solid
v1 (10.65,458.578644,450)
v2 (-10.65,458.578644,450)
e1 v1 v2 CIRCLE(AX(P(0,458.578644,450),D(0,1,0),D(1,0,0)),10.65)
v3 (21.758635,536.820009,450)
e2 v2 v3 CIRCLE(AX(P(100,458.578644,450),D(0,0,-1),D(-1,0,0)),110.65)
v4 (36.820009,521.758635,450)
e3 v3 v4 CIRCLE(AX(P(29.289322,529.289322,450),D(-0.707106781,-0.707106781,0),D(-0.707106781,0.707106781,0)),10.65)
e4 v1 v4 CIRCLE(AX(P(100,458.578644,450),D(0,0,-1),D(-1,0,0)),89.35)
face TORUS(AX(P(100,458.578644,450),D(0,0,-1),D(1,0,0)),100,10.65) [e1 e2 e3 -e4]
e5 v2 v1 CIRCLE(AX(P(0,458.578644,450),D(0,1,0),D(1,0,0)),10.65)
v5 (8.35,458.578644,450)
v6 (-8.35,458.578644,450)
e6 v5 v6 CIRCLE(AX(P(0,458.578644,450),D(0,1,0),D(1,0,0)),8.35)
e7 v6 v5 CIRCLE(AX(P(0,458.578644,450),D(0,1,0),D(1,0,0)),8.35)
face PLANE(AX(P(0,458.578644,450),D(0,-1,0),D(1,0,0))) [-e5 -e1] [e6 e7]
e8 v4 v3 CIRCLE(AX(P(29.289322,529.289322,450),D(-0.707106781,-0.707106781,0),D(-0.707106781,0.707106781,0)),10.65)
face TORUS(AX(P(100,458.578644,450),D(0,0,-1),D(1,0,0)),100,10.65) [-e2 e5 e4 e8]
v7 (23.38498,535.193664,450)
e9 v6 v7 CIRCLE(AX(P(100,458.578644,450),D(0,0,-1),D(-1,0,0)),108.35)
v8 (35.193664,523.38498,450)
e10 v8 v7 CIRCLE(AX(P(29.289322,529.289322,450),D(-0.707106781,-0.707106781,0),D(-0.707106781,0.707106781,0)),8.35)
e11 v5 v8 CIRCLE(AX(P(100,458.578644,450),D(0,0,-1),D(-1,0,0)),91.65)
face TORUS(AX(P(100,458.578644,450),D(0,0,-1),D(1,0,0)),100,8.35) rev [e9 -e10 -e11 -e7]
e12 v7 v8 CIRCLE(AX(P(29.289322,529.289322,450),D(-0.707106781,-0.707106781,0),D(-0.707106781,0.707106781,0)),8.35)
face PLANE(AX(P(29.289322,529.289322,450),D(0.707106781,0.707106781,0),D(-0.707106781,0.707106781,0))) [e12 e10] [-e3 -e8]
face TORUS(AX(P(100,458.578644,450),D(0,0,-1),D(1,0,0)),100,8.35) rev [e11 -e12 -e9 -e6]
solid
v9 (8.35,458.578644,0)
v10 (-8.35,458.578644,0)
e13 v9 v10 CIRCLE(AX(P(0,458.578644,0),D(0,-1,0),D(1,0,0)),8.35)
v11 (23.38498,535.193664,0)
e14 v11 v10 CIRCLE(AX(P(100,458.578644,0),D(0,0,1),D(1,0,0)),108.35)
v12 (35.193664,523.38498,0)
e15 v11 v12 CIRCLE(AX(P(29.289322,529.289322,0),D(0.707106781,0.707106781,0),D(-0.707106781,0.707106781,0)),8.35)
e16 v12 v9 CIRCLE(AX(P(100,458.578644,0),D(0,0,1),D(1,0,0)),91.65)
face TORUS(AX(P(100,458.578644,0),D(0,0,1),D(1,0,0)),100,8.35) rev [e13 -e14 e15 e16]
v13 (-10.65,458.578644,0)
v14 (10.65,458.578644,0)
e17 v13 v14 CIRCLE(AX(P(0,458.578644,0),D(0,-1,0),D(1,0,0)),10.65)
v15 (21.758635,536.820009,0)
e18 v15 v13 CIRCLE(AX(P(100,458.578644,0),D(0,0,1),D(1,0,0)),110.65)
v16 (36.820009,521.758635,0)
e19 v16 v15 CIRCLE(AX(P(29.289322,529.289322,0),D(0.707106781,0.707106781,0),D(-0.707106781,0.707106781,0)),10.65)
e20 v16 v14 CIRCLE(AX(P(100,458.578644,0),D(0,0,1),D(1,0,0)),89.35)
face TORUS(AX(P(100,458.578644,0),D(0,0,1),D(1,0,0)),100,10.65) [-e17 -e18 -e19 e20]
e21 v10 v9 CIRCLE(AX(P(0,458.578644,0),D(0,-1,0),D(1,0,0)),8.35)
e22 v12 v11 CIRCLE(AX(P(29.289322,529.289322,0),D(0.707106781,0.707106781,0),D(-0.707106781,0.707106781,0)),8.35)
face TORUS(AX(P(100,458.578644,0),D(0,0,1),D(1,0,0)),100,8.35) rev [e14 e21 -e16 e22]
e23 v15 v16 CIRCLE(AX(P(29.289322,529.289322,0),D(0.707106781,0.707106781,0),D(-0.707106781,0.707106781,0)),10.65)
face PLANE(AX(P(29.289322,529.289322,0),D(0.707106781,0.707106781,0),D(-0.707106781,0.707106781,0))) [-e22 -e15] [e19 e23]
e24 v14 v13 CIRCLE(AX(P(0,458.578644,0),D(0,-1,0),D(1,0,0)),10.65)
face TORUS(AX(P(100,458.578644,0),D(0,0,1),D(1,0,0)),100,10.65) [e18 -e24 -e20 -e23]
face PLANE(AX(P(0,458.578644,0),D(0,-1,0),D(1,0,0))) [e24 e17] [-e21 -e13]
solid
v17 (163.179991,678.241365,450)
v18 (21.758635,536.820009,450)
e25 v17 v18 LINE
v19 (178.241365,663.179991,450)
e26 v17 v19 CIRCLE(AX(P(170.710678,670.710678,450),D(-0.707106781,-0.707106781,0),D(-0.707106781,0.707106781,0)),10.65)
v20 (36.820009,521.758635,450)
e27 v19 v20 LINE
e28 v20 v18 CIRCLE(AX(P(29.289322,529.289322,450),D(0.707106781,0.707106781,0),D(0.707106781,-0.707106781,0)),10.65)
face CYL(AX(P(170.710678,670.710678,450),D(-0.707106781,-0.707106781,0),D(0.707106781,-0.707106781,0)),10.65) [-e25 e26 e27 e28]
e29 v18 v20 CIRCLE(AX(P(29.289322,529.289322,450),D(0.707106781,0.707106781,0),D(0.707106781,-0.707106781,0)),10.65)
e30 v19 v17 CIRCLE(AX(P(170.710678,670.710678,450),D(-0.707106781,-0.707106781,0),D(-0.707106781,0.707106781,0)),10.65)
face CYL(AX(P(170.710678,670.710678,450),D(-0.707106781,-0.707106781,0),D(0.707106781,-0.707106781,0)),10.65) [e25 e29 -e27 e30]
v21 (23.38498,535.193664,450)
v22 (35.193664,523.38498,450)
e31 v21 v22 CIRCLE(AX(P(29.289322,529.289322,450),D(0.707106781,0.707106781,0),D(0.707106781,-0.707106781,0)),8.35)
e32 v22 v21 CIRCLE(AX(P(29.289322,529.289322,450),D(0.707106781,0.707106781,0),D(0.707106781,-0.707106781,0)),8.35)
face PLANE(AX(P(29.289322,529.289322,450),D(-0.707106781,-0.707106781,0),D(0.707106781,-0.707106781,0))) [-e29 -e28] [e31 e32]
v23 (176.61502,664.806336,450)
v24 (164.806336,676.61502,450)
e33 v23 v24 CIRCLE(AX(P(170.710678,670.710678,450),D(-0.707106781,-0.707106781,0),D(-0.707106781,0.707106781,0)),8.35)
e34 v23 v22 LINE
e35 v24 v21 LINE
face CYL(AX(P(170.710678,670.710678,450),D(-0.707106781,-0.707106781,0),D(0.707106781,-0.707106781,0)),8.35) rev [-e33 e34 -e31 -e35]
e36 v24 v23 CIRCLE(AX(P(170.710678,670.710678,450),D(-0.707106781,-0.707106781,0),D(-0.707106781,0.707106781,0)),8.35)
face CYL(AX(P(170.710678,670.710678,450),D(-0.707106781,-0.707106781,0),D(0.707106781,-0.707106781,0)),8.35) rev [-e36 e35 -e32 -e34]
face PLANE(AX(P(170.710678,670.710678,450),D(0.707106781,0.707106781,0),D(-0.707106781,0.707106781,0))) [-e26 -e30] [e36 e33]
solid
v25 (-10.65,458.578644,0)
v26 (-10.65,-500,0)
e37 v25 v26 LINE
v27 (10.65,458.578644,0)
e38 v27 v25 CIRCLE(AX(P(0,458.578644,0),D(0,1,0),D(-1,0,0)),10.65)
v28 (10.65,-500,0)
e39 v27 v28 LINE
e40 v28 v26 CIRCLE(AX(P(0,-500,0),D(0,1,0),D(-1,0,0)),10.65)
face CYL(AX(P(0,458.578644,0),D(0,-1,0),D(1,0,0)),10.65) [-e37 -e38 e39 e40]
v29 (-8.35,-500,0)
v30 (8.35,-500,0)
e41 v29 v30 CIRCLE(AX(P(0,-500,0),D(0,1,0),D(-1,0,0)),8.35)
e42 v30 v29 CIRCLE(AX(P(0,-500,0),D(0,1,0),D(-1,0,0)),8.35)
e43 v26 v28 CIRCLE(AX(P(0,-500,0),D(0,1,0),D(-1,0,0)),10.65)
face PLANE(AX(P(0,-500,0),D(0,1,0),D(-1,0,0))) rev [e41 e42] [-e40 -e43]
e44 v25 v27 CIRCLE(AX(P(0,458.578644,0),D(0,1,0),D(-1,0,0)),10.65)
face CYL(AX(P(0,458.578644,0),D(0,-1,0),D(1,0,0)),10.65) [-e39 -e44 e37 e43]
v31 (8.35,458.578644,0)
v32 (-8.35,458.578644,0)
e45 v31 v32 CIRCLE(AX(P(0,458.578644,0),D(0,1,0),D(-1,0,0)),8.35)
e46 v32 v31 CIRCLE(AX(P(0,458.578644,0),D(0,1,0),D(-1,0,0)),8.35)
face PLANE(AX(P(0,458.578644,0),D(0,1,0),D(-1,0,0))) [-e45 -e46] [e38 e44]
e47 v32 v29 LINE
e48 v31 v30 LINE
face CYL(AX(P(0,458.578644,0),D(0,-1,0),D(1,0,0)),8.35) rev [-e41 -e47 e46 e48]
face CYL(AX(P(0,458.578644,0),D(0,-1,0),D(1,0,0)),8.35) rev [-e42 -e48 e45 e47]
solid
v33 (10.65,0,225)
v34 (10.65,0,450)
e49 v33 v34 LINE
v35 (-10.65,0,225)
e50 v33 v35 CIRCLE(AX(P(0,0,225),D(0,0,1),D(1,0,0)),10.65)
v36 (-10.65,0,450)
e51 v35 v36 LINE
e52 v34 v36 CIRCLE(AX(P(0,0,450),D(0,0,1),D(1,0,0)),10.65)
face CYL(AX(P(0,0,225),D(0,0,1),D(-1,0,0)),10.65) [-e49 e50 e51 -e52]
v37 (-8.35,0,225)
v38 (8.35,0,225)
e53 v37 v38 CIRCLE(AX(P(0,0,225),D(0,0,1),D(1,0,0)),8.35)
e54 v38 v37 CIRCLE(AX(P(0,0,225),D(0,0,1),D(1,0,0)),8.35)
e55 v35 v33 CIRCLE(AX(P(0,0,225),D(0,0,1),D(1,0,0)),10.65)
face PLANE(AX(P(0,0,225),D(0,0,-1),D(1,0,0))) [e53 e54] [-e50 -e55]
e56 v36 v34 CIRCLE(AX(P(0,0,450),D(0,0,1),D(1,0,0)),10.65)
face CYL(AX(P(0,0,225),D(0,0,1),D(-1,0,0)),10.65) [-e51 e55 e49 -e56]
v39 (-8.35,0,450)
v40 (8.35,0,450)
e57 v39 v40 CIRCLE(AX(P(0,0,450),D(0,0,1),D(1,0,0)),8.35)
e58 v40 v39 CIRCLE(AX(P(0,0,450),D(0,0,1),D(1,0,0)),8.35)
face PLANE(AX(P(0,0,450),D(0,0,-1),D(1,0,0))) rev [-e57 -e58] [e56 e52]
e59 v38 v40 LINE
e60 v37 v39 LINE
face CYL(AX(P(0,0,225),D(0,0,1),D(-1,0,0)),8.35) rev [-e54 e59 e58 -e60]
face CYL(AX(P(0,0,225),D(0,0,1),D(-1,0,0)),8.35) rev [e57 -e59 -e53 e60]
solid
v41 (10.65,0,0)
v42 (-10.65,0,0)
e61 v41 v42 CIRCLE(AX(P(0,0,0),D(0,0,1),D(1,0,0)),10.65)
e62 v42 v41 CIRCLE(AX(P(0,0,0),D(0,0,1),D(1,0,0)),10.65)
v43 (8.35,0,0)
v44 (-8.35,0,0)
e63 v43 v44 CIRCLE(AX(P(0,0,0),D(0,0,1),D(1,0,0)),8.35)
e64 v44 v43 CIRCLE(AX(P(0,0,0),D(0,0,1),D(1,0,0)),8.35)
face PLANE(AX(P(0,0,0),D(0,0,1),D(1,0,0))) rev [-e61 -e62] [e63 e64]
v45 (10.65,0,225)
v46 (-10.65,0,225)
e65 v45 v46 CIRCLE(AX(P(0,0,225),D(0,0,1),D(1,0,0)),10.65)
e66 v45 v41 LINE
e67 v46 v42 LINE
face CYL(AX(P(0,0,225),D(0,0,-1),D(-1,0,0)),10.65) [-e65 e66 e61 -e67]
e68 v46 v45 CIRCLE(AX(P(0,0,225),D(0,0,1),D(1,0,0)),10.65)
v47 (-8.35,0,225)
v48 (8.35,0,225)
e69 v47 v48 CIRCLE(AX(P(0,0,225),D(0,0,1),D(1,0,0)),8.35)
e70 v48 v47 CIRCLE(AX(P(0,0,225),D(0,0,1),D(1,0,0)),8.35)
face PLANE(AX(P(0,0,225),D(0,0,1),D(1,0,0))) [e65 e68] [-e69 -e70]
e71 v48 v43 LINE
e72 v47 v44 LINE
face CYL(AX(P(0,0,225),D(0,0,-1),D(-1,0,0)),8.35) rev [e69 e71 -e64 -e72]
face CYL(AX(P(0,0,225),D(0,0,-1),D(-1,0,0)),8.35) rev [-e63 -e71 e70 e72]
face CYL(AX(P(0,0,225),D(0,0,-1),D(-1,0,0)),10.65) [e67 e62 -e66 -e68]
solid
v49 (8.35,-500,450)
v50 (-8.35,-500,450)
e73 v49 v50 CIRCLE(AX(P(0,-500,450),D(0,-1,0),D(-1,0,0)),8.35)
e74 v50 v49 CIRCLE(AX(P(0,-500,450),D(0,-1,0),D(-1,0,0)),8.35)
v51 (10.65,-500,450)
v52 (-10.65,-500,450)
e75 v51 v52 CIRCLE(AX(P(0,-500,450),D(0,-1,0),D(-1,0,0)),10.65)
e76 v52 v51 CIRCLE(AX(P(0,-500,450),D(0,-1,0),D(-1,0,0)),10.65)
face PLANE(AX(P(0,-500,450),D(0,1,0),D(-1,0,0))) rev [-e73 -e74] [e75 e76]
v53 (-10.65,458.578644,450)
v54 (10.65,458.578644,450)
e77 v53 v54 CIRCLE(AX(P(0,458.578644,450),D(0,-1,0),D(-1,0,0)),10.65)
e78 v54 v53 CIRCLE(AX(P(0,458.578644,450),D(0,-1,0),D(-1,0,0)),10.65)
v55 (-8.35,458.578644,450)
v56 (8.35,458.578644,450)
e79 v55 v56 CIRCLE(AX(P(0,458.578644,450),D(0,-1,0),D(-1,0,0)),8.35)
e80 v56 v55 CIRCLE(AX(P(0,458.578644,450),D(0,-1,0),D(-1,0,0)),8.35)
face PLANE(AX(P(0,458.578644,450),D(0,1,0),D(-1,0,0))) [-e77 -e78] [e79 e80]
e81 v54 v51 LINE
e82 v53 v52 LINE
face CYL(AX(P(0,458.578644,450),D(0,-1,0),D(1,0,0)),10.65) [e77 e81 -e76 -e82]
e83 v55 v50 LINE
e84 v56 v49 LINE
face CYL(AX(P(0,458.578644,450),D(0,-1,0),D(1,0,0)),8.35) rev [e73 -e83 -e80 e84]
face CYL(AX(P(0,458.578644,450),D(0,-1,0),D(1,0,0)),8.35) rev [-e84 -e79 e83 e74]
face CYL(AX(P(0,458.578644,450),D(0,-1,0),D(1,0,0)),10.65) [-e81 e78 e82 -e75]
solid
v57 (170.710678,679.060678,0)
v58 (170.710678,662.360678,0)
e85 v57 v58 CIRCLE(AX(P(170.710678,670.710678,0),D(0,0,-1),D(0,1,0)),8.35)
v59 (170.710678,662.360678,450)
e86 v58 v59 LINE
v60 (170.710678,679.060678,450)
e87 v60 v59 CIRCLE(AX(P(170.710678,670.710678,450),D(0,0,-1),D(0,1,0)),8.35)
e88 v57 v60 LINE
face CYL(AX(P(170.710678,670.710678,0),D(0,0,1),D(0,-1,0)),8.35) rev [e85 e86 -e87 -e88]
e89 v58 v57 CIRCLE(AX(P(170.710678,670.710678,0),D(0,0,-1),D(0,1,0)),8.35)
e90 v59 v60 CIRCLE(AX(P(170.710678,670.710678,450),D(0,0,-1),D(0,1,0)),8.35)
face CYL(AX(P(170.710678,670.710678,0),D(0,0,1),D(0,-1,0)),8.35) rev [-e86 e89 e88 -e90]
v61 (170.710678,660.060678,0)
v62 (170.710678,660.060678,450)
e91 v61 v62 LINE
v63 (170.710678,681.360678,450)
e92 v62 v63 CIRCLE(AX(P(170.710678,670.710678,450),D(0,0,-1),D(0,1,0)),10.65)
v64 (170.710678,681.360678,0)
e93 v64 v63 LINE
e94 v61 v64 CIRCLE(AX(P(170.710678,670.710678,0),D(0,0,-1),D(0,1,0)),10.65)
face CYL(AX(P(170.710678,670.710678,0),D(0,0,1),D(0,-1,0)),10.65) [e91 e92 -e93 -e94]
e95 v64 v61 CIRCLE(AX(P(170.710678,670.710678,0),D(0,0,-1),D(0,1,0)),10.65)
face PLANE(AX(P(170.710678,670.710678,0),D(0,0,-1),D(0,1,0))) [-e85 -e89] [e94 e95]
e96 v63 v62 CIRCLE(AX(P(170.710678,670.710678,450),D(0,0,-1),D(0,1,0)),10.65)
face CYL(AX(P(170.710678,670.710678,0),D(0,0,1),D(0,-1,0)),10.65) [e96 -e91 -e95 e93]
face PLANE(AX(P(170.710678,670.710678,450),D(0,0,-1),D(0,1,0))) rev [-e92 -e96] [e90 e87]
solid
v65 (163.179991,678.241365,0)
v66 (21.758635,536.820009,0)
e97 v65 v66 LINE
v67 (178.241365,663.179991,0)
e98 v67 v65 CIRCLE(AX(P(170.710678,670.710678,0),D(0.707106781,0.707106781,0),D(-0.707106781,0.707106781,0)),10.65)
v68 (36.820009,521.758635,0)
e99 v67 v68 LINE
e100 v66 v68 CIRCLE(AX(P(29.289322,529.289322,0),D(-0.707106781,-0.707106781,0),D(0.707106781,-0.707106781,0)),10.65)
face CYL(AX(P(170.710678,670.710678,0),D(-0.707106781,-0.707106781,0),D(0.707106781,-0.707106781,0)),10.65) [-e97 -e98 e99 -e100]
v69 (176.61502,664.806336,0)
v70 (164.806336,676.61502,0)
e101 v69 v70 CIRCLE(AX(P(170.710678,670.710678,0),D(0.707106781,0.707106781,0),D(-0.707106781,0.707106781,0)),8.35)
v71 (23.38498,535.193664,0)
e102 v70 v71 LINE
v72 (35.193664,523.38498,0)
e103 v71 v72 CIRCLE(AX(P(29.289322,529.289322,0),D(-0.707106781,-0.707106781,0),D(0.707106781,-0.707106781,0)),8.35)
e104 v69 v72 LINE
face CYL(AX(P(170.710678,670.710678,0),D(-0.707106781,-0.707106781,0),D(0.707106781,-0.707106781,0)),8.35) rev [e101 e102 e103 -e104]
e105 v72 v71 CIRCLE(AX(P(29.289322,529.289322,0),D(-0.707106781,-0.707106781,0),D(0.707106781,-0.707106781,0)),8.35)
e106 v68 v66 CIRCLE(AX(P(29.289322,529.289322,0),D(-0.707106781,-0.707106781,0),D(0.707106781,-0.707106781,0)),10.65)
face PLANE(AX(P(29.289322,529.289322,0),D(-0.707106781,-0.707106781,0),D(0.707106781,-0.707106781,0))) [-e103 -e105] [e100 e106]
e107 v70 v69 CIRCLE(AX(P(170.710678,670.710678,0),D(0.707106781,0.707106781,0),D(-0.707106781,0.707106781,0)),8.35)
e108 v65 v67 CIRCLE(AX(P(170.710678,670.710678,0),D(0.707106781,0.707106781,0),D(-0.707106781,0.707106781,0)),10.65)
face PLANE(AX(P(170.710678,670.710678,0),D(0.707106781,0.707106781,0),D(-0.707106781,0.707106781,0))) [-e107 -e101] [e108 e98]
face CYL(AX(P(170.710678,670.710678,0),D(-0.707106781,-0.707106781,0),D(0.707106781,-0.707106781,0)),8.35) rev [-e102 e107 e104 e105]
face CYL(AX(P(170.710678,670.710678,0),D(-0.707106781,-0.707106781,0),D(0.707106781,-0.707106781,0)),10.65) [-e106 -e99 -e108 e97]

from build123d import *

# Parameters (mm, degrees)
SKETCH1_ON_SEGMENT_1_R    = 10.65
SKETCH1_ON_SEGMENT_1_R_2  = 8.35
PIPE_21_3_X_2_3_1_DEPTH   = 958.578643763
SKETCH1_ON_SEGMENT_2_R    = 10.65
SKETCH1_ON_SEGMENT_2_R_2  = 8.35
PIPE_21_3_X_2_3_1_2_ANGLE = 45
SKETCH1_R                 = 10.65
SKETCH1_R_2               = 8.35
PIPE_21_3_X_2_3_1_3_DEPTH = 200
SKETCH11_R                = 10.65
SKETCH11_R_2              = 8.35
PIPE_21_3_X_2_3_2_DEPTH   = 225
SKETCH12_R                = 10.65
SKETCH12_R_2              = 8.35
PIPE_21_3_X_2_3_3_DEPTH   = 450


with BuildPart() as part:
    # Sketch1 on segment 1 (carried to segment 1) → Pipe 21.3 X 2.3(1) (new body)
    with BuildSketch(Plane(origin=(0, -500, 0), x_dir=(-1, 0, 0), z_dir=(0, 1, 0))):
        Circle(SKETCH1_ON_SEGMENT_1_R)
        Circle(SKETCH1_ON_SEGMENT_1_R_2, mode=Mode.SUBTRACT)
    extrude(amount=PIPE_21_3_X_2_3_1_DEPTH)


with BuildPart() as body_2:
    # Sketch1 on segment 2 (carried to the start of arc 2) → Pipe 21.3 X 2.3_1 2 (revolve)
    with BuildSketch(Plane(origin=(29.289321881, 529.289321881, 0), x_dir=(0.707106781, -0.707106781, 0), z_dir=(-0.707106781, -0.707106781, 0))):
        Circle(SKETCH1_ON_SEGMENT_2_R)
        Circle(SKETCH1_ON_SEGMENT_2_R_2, mode=Mode.SUBTRACT)
    revolve(axis=Axis((100, 458.578643763, 0), (0, 0, 1)), revolution_arc=PIPE_21_3_X_2_3_1_2_ANGLE)


with BuildPart() as body_3:
    # Sketch1 → Pipe 21.3 X 2.3_1 3 (new body)
    with BuildSketch(Plane(origin=(29.289321881, 529.289321881, 0), x_dir=(-0.7071067811865461, 0.7071067811865489, 0), z_dir=(0.7071067811865489, 0.7071067811865461, 0))):
        Circle(SKETCH1_R)
        Circle(SKETCH1_R_2, mode=Mode.SUBTRACT)
    extrude(amount=PIPE_21_3_X_2_3_1_3_DEPTH)


with BuildPart() as body_4:
    # Sketch11 → Pipe 21.3 X 2.3(2) (new body)
    with BuildSketch(Plane(origin=(0, 0, 0), x_dir=(0, -1, 0), z_dir=(0, 0, 1))):
        Circle(SKETCH11_R)
        Circle(SKETCH11_R_2, mode=Mode.SUBTRACT)
    extrude(amount=PIPE_21_3_X_2_3_2_DEPTH)


with BuildPart() as body_5:
    # Mirror1: mirrored copy
    add(body_3.part.mirror(Plane.XY.offset(225)))


with BuildPart() as body_6:
    # Mirror1 2: mirrored copy
    add(body_2.part.mirror(Plane.XY.offset(225)))


with BuildPart() as body_7:
    # Mirror1 3: mirrored copy
    add(part.part.mirror(Plane.XY.offset(225)))


with BuildPart() as body_8:
    # Mirror1 4: mirrored copy
    add(body_4.part.mirror(Plane.XY.offset(225)))


with BuildPart() as body_9:
    # Sketch12 → Pipe 21.3 X 2.3(3) (new body)
    with BuildSketch(Plane(origin=(170.710678119, 670.710678119, 450), x_dir=(-0.7071067811865461, 0.7071067811865489, 0), z_dir=(0, 0, -1))):
        Circle(SKETCH12_R)
        Circle(SKETCH12_R_2, mode=Mode.SUBTRACT)
    extrude(amount=PIPE_21_3_X_2_3_3_DEPTH)


solid = Compound([part.part, body_2.part, body_3.part, body_4.part, body_5.part, body_6.part, body_7.part, body_8.part, body_9.part])
